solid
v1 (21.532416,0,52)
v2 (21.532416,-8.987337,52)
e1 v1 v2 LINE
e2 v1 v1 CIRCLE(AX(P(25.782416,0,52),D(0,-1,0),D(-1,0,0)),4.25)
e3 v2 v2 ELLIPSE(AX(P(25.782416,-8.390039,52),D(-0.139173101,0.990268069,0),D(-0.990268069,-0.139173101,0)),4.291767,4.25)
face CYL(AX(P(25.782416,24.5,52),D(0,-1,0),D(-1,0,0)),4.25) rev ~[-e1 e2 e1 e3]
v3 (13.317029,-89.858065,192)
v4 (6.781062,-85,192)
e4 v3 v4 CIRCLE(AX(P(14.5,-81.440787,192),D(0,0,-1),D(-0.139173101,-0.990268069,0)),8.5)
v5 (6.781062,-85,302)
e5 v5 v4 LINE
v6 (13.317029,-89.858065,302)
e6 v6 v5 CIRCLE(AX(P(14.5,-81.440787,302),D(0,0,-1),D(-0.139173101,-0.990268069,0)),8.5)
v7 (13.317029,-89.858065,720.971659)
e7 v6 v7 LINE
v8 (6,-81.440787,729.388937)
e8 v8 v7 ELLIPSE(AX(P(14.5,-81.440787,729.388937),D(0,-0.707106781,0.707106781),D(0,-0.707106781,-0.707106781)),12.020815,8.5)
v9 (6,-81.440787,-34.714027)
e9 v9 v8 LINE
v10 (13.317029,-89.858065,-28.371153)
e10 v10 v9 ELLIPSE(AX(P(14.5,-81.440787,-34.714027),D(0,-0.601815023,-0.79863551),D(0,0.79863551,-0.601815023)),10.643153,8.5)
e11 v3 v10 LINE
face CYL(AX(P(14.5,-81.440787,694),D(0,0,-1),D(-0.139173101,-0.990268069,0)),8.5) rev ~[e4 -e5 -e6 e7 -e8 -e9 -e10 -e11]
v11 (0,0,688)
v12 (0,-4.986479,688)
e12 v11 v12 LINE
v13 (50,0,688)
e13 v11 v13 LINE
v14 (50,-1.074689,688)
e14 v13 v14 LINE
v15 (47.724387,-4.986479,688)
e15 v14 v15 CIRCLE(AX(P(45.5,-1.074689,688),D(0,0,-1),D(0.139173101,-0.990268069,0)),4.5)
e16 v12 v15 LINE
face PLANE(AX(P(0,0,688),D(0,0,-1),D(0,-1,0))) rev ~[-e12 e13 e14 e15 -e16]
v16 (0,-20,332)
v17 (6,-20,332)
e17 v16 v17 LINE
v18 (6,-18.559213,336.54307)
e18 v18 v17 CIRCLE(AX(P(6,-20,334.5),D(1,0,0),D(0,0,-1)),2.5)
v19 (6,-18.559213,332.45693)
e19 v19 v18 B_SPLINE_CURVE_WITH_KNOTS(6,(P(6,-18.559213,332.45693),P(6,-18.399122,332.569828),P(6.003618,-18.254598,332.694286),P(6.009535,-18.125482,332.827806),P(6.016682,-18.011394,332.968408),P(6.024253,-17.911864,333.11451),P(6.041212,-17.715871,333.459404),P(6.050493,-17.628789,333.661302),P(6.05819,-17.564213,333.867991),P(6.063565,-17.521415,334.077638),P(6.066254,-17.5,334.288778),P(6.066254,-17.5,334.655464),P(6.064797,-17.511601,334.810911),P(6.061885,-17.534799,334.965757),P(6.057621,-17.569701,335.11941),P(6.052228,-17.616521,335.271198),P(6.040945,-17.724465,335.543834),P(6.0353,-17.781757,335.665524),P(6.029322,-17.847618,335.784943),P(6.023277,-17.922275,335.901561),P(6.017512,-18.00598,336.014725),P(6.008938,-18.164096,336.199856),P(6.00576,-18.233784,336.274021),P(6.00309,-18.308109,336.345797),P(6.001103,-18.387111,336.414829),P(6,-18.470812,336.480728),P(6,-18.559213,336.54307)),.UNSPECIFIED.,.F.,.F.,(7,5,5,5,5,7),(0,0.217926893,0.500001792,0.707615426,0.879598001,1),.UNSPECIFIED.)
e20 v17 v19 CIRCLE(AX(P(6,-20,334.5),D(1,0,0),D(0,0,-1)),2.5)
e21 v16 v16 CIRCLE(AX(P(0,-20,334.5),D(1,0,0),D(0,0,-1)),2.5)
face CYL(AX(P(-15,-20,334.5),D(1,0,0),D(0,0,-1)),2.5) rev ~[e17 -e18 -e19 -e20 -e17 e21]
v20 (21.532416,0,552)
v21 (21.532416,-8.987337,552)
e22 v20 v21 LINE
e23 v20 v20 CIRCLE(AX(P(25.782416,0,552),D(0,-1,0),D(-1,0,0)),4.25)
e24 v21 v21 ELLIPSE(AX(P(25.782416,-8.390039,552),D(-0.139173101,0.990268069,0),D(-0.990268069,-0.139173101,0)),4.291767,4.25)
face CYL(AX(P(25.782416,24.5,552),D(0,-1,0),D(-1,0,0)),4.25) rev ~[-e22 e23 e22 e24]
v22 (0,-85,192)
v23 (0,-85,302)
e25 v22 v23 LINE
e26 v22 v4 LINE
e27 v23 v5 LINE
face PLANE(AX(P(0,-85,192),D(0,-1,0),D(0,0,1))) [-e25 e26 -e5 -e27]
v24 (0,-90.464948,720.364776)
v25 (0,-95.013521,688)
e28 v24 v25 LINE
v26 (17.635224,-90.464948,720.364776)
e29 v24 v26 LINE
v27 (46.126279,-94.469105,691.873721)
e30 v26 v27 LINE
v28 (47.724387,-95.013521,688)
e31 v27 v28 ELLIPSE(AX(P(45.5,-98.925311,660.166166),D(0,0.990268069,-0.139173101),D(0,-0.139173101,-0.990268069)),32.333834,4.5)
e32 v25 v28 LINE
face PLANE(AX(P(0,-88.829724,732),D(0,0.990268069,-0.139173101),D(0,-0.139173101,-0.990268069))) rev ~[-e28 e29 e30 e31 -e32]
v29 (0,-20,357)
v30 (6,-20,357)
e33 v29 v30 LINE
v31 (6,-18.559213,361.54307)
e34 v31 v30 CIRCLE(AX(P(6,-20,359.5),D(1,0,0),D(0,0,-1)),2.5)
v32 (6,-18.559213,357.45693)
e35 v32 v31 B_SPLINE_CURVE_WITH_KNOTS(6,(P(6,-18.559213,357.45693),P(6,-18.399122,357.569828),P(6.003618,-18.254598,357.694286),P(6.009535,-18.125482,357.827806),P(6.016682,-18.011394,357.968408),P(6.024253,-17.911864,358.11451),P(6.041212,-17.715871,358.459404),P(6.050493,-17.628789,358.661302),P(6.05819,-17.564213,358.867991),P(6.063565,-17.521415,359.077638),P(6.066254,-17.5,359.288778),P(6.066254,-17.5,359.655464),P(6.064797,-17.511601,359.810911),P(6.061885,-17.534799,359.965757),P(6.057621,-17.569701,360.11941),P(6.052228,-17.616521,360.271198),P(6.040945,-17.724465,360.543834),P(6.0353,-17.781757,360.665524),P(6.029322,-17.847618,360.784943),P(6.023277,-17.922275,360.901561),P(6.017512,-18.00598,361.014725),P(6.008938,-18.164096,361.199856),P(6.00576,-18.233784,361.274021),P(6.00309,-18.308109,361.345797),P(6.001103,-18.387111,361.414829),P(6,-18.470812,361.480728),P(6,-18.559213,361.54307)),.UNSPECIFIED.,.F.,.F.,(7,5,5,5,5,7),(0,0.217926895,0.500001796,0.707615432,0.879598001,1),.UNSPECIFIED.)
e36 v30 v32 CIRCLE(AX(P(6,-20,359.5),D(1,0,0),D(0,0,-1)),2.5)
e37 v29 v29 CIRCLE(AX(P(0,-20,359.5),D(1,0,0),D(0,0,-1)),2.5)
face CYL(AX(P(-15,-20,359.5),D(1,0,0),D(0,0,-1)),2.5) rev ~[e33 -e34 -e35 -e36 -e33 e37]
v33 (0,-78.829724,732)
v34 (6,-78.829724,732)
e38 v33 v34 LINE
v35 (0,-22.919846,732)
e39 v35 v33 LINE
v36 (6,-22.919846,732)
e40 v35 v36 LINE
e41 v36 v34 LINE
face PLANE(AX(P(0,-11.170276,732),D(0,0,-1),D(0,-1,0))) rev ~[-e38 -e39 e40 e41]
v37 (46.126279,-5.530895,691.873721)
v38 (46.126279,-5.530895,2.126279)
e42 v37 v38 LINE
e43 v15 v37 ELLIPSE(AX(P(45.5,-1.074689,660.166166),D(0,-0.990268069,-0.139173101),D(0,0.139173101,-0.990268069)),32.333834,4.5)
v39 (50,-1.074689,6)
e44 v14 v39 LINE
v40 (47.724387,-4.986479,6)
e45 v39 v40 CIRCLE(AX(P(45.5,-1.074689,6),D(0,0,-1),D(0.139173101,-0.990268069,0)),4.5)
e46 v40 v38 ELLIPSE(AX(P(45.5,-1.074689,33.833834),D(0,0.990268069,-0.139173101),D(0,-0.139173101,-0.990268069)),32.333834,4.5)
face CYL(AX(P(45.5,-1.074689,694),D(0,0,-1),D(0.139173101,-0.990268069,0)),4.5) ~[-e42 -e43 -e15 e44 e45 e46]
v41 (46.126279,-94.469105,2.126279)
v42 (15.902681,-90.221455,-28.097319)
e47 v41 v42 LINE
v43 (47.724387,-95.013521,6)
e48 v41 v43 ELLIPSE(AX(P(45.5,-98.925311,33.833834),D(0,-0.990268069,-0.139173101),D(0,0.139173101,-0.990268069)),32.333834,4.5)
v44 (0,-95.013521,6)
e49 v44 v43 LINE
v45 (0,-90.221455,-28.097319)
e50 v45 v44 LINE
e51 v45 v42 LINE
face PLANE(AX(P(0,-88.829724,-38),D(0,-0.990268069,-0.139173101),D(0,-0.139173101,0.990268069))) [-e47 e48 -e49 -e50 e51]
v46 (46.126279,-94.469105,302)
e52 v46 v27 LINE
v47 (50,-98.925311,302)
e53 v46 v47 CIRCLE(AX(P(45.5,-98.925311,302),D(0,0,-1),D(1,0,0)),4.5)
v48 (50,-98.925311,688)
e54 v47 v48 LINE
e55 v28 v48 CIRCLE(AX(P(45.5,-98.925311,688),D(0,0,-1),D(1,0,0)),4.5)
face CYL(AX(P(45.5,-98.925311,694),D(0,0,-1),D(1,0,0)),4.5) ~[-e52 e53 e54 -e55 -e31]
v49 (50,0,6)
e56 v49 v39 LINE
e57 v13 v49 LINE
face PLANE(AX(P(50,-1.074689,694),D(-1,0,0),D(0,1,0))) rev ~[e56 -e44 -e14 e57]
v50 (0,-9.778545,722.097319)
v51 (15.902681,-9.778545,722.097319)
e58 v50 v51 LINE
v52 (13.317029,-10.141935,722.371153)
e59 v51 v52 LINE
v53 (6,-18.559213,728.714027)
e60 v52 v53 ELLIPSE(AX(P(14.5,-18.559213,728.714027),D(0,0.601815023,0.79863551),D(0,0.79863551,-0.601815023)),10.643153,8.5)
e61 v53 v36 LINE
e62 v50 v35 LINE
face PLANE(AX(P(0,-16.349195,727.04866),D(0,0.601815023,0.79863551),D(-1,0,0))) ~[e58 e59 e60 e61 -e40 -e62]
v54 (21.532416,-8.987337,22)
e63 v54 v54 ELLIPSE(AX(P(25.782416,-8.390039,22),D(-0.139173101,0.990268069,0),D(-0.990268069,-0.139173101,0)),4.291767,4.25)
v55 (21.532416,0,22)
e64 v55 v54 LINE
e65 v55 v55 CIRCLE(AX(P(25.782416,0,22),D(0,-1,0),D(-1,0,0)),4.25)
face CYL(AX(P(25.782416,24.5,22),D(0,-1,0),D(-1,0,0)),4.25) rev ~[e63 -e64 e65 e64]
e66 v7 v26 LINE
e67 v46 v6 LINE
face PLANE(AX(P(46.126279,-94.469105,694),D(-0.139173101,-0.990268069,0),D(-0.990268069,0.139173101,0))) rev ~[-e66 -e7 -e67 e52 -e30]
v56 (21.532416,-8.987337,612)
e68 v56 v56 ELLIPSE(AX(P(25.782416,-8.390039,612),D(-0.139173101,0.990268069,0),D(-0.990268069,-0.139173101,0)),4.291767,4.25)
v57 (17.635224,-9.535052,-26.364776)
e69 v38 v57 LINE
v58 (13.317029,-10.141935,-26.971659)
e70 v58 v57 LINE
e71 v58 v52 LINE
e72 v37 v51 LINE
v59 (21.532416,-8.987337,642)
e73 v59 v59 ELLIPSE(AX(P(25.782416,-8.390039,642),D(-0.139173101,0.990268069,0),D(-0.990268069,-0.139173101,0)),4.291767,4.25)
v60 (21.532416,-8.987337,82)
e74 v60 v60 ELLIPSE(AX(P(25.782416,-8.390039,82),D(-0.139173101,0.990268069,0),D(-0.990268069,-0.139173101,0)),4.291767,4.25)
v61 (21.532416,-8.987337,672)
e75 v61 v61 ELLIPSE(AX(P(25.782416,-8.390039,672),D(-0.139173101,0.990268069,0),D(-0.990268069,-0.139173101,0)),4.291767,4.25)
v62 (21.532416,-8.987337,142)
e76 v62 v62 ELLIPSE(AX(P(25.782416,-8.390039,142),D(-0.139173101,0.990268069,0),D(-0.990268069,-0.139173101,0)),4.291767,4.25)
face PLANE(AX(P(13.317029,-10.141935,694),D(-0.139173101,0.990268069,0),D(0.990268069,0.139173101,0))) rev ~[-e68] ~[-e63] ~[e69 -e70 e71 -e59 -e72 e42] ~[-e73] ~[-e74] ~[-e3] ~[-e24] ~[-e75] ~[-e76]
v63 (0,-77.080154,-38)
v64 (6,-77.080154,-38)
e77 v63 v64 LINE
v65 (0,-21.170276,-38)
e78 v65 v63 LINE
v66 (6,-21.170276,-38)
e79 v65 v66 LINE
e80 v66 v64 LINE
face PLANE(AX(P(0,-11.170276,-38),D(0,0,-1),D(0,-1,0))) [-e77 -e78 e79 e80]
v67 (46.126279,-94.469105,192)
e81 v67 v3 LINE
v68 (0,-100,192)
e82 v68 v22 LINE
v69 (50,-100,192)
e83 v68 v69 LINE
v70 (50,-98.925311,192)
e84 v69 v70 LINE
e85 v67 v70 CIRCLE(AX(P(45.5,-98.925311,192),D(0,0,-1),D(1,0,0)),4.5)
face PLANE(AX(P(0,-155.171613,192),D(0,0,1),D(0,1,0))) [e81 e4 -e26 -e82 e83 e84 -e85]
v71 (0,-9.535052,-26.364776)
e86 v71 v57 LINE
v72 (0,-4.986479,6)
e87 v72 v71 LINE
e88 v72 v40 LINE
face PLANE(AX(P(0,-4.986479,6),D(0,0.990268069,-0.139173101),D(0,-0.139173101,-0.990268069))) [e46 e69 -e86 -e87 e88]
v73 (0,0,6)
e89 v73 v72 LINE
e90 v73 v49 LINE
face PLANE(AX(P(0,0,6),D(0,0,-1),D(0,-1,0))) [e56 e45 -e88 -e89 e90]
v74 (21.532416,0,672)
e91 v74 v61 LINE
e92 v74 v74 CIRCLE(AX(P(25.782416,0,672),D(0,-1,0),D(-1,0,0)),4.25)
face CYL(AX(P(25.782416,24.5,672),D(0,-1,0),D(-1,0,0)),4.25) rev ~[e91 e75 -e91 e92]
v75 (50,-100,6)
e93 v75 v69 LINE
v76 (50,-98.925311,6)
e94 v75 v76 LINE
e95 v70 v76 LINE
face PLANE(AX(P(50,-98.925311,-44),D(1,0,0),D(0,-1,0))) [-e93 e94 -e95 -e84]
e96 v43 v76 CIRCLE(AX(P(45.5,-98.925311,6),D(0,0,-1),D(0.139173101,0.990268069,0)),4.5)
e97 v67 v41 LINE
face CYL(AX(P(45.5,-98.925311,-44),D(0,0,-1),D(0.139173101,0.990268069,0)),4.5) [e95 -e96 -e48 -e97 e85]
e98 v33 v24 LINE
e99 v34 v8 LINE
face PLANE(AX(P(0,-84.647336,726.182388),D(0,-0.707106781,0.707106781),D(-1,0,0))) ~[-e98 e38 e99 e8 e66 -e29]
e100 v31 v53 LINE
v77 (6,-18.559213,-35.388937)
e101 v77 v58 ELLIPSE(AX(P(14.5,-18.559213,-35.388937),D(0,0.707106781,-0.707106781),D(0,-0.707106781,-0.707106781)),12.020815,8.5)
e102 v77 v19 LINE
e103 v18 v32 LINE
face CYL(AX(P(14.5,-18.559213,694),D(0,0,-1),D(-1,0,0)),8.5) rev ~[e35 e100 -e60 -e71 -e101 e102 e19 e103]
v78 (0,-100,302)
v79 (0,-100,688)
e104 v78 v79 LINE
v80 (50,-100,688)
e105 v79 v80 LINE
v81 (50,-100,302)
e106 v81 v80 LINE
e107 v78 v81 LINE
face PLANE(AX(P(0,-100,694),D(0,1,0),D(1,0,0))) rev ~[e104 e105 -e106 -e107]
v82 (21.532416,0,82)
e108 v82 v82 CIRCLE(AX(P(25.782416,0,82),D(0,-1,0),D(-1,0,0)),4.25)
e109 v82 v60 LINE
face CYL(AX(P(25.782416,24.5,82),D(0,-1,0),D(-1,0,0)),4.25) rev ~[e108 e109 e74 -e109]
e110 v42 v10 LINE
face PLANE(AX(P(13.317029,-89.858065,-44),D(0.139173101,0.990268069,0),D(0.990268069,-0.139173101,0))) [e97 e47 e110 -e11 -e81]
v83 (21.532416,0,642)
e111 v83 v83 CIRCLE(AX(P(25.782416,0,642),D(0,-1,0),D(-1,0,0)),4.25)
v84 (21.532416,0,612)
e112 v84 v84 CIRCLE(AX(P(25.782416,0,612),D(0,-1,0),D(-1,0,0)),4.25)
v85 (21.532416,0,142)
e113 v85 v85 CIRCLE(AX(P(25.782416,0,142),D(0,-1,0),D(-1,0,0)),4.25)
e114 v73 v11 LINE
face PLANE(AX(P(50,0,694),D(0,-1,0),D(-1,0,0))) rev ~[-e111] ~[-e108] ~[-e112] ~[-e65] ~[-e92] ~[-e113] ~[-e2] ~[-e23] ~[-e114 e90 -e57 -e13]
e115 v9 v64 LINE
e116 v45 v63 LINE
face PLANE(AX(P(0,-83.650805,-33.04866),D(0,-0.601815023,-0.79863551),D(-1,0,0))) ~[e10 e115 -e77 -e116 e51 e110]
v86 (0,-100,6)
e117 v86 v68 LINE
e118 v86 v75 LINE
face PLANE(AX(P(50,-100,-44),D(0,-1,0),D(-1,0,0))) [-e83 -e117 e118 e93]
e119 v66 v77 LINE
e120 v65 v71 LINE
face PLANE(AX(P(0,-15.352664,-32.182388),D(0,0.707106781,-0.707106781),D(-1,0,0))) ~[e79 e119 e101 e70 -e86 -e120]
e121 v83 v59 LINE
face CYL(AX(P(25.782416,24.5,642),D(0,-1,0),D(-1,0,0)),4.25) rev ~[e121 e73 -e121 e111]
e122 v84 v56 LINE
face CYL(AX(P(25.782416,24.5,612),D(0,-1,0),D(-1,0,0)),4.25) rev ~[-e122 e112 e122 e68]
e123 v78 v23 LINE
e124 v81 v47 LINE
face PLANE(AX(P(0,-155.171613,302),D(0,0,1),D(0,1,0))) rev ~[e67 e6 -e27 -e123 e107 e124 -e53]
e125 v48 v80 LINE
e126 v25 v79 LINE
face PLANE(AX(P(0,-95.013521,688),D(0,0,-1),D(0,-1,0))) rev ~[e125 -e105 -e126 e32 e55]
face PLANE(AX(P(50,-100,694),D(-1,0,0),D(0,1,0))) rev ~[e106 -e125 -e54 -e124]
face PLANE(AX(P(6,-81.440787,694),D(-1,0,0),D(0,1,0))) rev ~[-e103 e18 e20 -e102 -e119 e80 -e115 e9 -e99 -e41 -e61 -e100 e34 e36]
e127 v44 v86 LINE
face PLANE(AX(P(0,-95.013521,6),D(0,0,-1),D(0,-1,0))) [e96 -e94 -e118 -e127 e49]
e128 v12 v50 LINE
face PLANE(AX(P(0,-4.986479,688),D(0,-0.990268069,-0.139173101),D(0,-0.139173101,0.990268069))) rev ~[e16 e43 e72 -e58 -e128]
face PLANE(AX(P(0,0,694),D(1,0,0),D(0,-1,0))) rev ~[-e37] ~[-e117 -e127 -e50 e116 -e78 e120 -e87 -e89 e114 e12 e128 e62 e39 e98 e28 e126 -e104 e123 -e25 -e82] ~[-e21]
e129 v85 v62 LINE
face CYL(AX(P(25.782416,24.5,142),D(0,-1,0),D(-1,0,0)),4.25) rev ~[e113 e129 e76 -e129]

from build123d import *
from OCP.BRepFilletAPI import BRepFilletAPI_MakeChamfer

# Parameters (mm, degrees)
BOSS_EXTRUDE1_DEPTH    = 694
SKETCH3_W              = 110
SKETCH3_H              = 70.171613021
CUT_EXTRUDE1_DEPTH     = 145
M10_TAPPED_HOLE2_D     = 8.5
M10_TAPPED_HOLE2_DEPTH = 24.5
M10_TAPPED_HOLE2_TIP   = 2.553657631
BOSS_EXTRUDE2_START    = 44
BOSS_EXTRUDE2_DEPTH    = 44
BOSS_EXTRUDE3_DEPTH    = 44
CUT_EXTRUDE3_DEPTH     = 100
CHAMFER1_SIZE          = 10
CHAMFER1_SIZE2         = 11.749570117
M6_TAPPED_HOLE1_D      = 5
M6_TAPPED_HOLE1_DEPTH  = 15
M6_TAPPED_HOLE1_TIP    = 1.502151548


with BuildPart() as part:
    # Sketch1 → Boss-Extrude1 (new body)
    with BuildSketch(Plane.XY):
        with BuildLine():
            Line((0, 0), (0, -100))
            Line((0, -100), (50, -100))
            Line((50, -100), (50, -98.925311188))
            ThreePointArc((50, -98.925311188), (48.896193111, -95.973045557), (46.126278954, -94.469104878))
            Line((46.126278954, -94.469104878), (13.317028642, -89.858065454))
            ThreePointArc((13.317028642, -89.858065454), (8.084968568, -87.017288616), (6, -81.440786869))
            Line((6, -81.440786869), (6, -18.559213131))
            ThreePointArc((6, -18.559213131), (8.084968568, -12.982711384), (13.317028642, -10.141934546))
            Line((13.317028642, -10.141934546), (46.126278954, -5.530895122))
            ThreePointArc((46.126278954, -5.530895122), (48.896193111, -4.026954443), (50, -1.074688812))
            Line((50, -1.074688812), (50, 0))
            Line((50, 0), (0, 0))
        make_face()
    extrude(amount=BOSS_EXTRUDE1_DEPTH)

    # Sketch3 → Cut-Extrude1 (cut)
    with BuildSketch(Plane.ZY):
        with Locations((247, -120.085806511)):
            Rectangle(SKETCH3_W, SKETCH3_H)
    extrude(amount=-CUT_EXTRUDE1_DEPTH, mode=Mode.SUBTRACT)

    # M10 Tapped Hole2
    with Locations(Plane(origin=(0, 0, 0), x_dir=(1, 0, 0), z_dir=(0, 1, 0))):
        with Locations((25.782416052, -142), (25.782416052, -82), (25.782416052, -22), (25.782416052, -52), (25.782416052, -552), (25.782416052, -612), (25.782416052, -642), (25.782416052, -672)):
            Hole(M10_TAPPED_HOLE2_D / 2, depth=M10_TAPPED_HOLE2_DEPTH)
            with Locations((0, 0, -(M10_TAPPED_HOLE2_DEPTH + M10_TAPPED_HOLE2_TIP / 2))):  # 118° drill point
                Cone(0, M10_TAPPED_HOLE2_D / 2, M10_TAPPED_HOLE2_TIP, mode=Mode.SUBTRACT)

    # Sketch15 → Boss-Extrude2 (add)
    with BuildSketch(Plane(origin=(0, 0, 0), x_dir=(-1, 0, 0), z_dir=(0, 0, -1)).offset(BOSS_EXTRUDE2_START)):
        with BuildLine():
            Line((0, 0), (-50, 0))
            Line((-50, 0), (-50, -1.074688812))
            ThreePointArc((-50, -1.074688812), (-48.896193111, -4.026954443), (-46.126278954, -5.530895122))
            Line((-46.126278954, -5.530895122), (-13.317028642, -10.141934546))
            ThreePointArc((-13.317028642, -10.141934546), (-8.084968568, -12.982711384), (-6, -18.559213131))
            Line((-6, -18.559213131), (-6, -81.440786869))
            ThreePointArc((-6, -81.440786869), (-8.084968568, -87.017288616), (-13.317028642, -89.858065454))
            Line((-13.317028642, -89.858065454), (-46.126278954, -94.469104878))
            ThreePointArc((-46.126278954, -94.469104878), (-48.896193111, -95.973045557), (-50, -98.925311188))
            Line((-50, -98.925311188), (-50, -100))
            Line((-50, -100), (0, -100))
            Line((0, -100), (0, 0))
        make_face()
    extrude(amount=-BOSS_EXTRUDE2_DEPTH)

    # Sketch17 → Boss-Extrude3 (add)
    with BuildSketch(Plane.XY.offset(694)):
        with BuildLine():
            Line((50, 0), (0, 0))
            Line((0, 0), (0, -100))
            Line((0, -100), (50, -100))
            Line((50, -100), (50, -98.925311188))
            ThreePointArc((50, -98.925311188), (48.896193111, -95.973045557), (46.126278954, -94.469104878))
            Line((46.126278954, -94.469104878), (13.317028642, -89.858065454))
            ThreePointArc((13.317028642, -89.858065454), (8.084968568, -87.017288616), (6, -81.440786869))
            Line((6, -81.440786869), (6, -18.559213131))
            ThreePointArc((6, -18.559213131), (8.084968568, -12.982711384), (13.317028642, -10.141934546))
            Line((13.317028642, -10.141934546), (46.126278954, -5.530895122))
            ThreePointArc((46.126278954, -5.530895122), (48.896193111, -4.026954443), (50, -1.074688812))
            Line((50, -1.074688812), (50, 0))
        make_face()
    extrude(amount=BOSS_EXTRUDE3_DEPTH)

    # Sketch16 → Cut-Extrude3 (cut)
    with BuildSketch(Plane.ZY):
        Polygon((6, -100), (-44, -100), (-44, 0), (6, 0), (6, -4.986479132), (-38, -11.170275859), (-38, -88.829724141), (6, -95.013520868), align=None)
        Polygon((688, -95.013520868), (688, -100), (738, -100), (738, 0), (688, 0), (688, -4.986479132), (732, -11.170275859), (732, -88.829724141), align=None)
    extrude(amount=-CUT_EXTRUDE3_DEPTH, mode=Mode.SUBTRACT)

    # Chamfer1: one chamfer whose edges measure the first distance from different faces: ONE call of the kernel's chamfer builder (chamfer() names one face for all edges)
    chamfer1_edges_1 = [part.edges().sort_by_distance(p)[0] for p in [
        (5.149190275, -11.170275859, 732),
    ]]
    chamfer1_side_1 = [part.faces().sort_by_distance(p)[0] for p in [
        (16.706788041, -7.313969364, 704.560953522),
    ]]
    chamfer1_edges_2 = [part.edges().sort_by_distance(p)[0] for p in [
        (5.149190275, -88.829724141, 732),
    ]]
    chamfer1_side_2 = [part.faces().sort_by_distance(p)[0] for p in [
        (3.160002327, -50, 732),
    ]]
    chamfer1_edges_3 = [part.edges().sort_by_distance(p)[0] for p in [
        (5.149190275, -11.170275859, -38),
    ]]
    chamfer1_side_3 = [part.faces().sort_by_distance(p)[0] for p in [
        (3.160002327, -50, -38),
    ]]
    chamfer1_edges_4 = [part.edges().sort_by_distance(p)[0] for p in [
        (5.149190275, -88.829724141, -38),
    ]]
    chamfer1_side_4 = [part.faces().sort_by_distance(p)[0] for p in [
        (16.706788041, -92.686030636, -10.560953522),
    ]]
    chamfer1 = BRepFilletAPI_MakeChamfer(part.part.solid().wrapped)
    for e in chamfer1_edges_1:
        chamfer1.Add(CHAMFER1_SIZE, CHAMFER1_SIZE2, e.wrapped, chamfer1_side_1[0].wrapped)  # the first distance lies on this face
    for e in chamfer1_edges_2:
        chamfer1.Add(CHAMFER1_SIZE, CHAMFER1_SIZE2, e.wrapped, chamfer1_side_2[0].wrapped)  # the first distance lies on this face
    for e in chamfer1_edges_3:
        chamfer1.Add(CHAMFER1_SIZE, CHAMFER1_SIZE2, e.wrapped, chamfer1_side_3[0].wrapped)  # the first distance lies on this face
    for e in chamfer1_edges_4:
        chamfer1.Add(CHAMFER1_SIZE, CHAMFER1_SIZE2, e.wrapped, chamfer1_side_4[0].wrapped)  # the first distance lies on this face
    add(Compound.cast(chamfer1.Shape()), mode=Mode.REPLACE)

    # M6 Tapped Hole1
    with Locations(Plane.ZY):
        with Locations((334.5, -20), (359.5, -20)):
            Hole(M6_TAPPED_HOLE1_D / 2, depth=M6_TAPPED_HOLE1_DEPTH)
            with Locations((0, 0, -(M6_TAPPED_HOLE1_DEPTH + M6_TAPPED_HOLE1_TIP / 2))):  # 118° drill point
                Cone(0, M6_TAPPED_HOLE1_D / 2, M6_TAPPED_HOLE1_TIP, mode=Mode.SUBTRACT)


solid = part.part
